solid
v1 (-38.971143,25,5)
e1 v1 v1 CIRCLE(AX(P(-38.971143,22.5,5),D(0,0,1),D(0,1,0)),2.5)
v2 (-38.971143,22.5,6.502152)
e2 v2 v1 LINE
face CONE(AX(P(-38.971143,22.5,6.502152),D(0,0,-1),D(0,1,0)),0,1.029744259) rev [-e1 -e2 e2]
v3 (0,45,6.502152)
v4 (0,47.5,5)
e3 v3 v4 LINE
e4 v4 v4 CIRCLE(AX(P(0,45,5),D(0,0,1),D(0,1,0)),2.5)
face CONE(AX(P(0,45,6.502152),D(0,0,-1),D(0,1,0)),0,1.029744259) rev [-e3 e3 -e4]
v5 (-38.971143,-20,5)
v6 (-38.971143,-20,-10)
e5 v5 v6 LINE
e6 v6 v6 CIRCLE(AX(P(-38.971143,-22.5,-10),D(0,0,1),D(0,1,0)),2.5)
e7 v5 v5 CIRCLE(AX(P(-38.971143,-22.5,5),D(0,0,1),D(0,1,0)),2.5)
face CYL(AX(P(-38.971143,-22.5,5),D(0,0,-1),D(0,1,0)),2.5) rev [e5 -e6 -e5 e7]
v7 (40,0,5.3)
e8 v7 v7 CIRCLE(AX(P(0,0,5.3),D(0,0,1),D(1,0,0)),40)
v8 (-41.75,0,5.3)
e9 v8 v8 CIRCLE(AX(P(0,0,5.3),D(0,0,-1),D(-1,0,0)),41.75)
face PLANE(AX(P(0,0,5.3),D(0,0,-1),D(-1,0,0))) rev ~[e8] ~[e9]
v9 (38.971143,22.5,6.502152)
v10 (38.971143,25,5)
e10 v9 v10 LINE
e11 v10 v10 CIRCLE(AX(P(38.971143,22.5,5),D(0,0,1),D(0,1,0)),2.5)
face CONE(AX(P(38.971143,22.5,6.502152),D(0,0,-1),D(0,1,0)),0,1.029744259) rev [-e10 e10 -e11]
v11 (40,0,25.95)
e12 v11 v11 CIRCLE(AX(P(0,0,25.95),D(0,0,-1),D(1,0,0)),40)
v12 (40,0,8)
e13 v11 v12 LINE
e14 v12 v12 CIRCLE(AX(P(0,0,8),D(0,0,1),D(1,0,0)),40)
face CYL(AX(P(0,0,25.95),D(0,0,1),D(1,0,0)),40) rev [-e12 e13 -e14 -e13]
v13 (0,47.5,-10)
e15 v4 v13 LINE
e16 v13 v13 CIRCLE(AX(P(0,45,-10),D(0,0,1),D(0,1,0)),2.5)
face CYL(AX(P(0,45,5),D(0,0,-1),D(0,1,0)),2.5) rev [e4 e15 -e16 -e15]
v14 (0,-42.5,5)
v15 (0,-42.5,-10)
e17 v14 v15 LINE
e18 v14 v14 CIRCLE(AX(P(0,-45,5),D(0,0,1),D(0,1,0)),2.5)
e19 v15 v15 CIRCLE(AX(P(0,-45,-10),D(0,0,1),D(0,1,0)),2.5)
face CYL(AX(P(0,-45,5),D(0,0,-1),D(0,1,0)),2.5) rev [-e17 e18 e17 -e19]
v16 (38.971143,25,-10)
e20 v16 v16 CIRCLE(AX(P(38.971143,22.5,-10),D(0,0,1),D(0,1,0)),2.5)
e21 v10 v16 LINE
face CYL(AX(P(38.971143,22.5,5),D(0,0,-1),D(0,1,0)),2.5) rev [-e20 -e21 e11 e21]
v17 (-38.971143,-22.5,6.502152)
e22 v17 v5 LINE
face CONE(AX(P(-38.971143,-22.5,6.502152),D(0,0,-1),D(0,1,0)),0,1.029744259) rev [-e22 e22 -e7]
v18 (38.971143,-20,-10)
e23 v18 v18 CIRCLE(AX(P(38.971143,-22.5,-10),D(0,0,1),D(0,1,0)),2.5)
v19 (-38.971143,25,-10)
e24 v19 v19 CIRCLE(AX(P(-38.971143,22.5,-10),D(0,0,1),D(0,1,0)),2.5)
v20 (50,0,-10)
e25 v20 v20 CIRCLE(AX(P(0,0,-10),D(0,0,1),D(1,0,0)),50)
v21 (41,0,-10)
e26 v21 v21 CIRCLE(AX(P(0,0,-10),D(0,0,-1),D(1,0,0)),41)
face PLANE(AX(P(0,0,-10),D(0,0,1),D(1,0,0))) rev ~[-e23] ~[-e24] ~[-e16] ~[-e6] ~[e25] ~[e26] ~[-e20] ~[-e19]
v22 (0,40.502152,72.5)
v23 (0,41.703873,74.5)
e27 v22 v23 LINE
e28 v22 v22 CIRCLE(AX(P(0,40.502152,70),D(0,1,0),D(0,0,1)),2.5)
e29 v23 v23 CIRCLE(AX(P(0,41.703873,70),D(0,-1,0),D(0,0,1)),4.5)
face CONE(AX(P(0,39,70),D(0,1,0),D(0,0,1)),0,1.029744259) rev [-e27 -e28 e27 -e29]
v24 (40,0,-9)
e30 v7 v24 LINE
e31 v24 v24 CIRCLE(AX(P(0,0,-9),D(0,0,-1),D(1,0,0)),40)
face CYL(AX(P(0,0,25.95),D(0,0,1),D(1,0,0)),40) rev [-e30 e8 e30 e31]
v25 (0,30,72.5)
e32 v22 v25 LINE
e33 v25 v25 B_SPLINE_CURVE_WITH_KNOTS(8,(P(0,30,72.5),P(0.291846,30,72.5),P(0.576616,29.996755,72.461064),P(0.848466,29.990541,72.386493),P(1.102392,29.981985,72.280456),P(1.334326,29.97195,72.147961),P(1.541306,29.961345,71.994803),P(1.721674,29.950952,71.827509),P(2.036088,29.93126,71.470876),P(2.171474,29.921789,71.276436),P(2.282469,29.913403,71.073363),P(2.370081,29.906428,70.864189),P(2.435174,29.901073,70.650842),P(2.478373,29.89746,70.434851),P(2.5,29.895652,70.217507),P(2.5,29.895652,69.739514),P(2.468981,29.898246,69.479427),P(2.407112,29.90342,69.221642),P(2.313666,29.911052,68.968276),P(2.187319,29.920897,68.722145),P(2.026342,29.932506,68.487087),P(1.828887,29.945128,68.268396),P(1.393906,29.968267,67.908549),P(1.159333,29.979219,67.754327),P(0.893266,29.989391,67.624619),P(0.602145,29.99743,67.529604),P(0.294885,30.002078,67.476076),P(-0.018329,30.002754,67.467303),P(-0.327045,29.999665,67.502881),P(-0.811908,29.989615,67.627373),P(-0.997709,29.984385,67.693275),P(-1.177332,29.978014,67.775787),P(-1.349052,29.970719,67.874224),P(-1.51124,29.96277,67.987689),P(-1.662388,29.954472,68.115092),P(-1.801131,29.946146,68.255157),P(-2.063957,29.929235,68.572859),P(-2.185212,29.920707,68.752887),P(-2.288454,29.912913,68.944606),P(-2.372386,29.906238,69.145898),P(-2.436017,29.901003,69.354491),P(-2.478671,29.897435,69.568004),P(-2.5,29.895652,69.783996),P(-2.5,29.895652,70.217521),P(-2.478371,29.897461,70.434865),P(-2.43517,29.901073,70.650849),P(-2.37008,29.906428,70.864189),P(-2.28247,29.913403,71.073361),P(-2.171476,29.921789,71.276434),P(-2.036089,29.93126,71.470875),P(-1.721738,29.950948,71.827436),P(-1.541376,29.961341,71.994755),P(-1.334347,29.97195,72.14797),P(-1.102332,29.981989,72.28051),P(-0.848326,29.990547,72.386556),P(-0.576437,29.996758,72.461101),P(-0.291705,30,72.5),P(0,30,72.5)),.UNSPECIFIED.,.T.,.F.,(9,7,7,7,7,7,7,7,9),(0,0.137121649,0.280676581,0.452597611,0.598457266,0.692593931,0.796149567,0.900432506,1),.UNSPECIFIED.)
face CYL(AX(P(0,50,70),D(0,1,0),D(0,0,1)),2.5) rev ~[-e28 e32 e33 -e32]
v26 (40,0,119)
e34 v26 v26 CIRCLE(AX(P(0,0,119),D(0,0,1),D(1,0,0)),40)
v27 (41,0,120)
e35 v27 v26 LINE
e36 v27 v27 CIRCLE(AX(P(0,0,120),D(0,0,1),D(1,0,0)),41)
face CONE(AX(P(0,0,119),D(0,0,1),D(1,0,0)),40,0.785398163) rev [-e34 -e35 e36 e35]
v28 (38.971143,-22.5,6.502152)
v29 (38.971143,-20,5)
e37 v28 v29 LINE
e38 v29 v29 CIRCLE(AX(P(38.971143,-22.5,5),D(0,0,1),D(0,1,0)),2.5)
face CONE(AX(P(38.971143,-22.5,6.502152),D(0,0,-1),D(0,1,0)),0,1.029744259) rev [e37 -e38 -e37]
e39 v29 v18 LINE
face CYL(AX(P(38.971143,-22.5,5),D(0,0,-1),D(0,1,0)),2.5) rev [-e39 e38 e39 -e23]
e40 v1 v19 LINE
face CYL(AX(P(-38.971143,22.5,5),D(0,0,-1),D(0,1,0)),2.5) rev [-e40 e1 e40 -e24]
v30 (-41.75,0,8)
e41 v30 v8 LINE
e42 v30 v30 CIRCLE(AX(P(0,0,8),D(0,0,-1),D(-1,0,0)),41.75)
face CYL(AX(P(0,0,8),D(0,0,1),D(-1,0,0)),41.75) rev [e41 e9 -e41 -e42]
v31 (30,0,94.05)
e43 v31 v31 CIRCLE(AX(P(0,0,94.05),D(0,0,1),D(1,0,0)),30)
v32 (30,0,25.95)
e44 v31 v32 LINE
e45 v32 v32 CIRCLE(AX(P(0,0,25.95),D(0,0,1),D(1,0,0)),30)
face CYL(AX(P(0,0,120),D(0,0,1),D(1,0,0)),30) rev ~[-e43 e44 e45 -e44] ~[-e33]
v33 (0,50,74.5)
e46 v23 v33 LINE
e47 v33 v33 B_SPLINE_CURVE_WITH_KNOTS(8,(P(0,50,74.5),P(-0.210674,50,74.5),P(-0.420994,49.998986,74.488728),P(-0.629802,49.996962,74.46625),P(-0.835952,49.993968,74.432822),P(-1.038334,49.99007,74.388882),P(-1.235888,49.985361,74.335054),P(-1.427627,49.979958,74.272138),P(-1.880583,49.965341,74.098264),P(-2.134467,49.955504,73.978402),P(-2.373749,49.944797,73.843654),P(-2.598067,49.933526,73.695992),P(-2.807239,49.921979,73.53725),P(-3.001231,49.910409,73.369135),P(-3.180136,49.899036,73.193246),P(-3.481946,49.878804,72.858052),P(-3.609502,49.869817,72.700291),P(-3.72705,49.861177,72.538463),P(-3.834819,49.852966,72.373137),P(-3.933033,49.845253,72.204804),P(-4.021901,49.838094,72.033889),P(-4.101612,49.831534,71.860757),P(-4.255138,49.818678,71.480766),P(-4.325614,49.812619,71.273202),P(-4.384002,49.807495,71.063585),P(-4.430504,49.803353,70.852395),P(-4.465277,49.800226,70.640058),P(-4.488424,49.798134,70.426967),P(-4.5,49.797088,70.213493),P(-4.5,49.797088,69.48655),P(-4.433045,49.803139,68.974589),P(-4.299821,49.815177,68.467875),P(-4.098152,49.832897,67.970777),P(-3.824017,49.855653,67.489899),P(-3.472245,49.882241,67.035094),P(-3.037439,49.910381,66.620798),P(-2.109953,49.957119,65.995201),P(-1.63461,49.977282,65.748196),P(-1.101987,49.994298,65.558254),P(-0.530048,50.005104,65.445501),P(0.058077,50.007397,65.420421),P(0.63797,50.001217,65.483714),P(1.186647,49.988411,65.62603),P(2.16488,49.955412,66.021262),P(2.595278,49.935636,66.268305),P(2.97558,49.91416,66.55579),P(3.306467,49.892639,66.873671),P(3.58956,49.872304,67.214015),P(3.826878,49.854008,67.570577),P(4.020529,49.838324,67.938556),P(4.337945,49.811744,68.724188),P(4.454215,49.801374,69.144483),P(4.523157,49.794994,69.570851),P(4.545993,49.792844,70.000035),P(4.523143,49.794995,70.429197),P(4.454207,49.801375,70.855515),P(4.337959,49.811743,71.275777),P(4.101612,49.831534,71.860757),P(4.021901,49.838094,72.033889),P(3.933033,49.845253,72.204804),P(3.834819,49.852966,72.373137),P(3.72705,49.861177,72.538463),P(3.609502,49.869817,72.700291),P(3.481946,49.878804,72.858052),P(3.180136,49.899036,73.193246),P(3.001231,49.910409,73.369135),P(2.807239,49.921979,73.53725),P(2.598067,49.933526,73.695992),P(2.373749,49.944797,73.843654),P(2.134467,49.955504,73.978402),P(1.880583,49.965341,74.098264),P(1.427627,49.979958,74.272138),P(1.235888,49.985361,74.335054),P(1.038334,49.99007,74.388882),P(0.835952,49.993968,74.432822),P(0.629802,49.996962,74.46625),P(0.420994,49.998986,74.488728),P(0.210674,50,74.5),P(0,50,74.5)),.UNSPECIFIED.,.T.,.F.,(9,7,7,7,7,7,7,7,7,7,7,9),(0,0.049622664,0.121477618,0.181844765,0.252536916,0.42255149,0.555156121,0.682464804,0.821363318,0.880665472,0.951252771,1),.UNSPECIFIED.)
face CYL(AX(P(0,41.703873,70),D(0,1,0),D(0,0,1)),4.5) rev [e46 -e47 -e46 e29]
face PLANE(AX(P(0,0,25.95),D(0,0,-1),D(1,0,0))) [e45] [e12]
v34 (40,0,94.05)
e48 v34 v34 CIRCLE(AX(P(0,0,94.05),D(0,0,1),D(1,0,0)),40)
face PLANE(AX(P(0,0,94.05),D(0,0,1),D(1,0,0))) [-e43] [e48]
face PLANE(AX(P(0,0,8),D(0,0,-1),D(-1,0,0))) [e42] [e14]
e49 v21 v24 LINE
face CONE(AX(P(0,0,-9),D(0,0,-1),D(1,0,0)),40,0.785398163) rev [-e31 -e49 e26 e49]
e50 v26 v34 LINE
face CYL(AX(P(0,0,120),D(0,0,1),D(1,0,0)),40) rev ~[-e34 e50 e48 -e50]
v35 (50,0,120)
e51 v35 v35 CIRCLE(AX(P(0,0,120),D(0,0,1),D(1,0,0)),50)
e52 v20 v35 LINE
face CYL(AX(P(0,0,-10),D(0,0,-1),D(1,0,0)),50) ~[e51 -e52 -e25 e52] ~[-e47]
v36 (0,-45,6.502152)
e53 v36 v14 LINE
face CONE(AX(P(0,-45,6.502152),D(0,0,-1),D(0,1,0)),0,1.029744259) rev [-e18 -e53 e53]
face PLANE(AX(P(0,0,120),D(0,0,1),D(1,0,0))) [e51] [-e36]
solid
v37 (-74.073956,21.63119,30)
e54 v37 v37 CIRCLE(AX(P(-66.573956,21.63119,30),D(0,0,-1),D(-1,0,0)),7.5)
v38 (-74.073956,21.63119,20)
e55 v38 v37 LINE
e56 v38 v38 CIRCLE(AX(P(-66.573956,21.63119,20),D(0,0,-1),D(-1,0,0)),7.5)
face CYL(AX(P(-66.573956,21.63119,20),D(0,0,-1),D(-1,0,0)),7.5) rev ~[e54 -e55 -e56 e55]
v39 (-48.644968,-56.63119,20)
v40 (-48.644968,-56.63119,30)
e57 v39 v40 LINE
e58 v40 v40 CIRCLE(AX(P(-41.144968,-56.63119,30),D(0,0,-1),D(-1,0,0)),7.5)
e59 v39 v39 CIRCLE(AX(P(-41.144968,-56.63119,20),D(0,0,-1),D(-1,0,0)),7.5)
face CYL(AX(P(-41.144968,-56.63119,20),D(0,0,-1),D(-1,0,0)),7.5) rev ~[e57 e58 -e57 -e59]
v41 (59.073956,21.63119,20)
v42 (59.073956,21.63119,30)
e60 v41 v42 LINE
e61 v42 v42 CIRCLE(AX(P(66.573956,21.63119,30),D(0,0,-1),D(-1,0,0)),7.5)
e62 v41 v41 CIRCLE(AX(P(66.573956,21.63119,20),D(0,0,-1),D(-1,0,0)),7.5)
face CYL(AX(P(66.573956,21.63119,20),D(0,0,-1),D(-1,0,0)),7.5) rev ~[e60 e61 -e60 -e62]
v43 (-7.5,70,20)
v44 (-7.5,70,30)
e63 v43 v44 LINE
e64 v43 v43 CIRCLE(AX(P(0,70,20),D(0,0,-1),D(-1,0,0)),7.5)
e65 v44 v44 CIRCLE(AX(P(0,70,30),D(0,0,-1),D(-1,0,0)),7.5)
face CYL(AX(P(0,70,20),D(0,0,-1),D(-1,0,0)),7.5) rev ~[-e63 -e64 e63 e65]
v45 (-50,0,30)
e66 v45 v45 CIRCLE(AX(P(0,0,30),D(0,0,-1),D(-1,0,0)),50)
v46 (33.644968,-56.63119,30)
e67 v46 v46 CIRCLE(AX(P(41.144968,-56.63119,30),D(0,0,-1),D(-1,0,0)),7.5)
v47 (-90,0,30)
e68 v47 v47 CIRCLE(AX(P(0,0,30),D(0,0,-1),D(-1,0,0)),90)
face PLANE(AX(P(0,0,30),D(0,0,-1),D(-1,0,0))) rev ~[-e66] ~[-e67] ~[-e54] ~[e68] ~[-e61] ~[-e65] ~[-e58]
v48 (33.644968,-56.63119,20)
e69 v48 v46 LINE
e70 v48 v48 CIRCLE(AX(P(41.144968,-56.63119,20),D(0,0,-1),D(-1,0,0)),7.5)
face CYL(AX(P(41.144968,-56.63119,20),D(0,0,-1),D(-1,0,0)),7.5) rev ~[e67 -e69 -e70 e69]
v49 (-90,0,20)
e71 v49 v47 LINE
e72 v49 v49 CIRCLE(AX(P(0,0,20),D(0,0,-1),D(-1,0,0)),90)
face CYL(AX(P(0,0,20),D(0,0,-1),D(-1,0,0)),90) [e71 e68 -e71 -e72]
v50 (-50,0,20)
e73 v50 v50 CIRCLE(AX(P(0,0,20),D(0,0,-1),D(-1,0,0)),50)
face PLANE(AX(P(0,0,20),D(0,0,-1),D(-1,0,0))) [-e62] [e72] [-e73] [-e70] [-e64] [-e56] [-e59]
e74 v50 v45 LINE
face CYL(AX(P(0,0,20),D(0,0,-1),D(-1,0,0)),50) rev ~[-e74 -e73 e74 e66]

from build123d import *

# Parameters (mm, degrees)
EXTRUDE_1_DEPTH             = 120
EXTRUDE_1_DEPTH_BACK        = 10
SKETCH_1_R                  = 50
SKETCH_2_R                  = 30
CUT_EXTRUDE_1_DEPTH         = 120
SKETCH_3_R                  = 40
CUT_EXTRUDE_2_DEPTH         = 25.95
CUT_EXTRUDE_START           = -35.95
SKETCH_4_R                  = 40
CUT_EXTRUDE_3_DEPTH         = 35.95
SKETCH_6_R                  = 90
SKETCH_6_R_2                = 50
EXTRUDE_2_DEPTH             = 10
SKETCH_7_R                  = 2.5
CUT_EXTRUDE_5_DEPTH         = 30
SKETCH_11_R                 = 7.5
CUT_EXTRUDE_6_DEPTH         = 10
CUT_EXTRUDE_START_2         = -2.7
SKETCH_12_R                 = 41.75
SKETCH_12_R_2               = 40
CUT_EXTRUDE_7_DEPTH         = 2.7
HOLE_WIZARD_M6_1_AT_2_COUNT = 2
HOLE_WIZARD_M6_1_AT_2_PITCH = 45
HOLE_WIZARD_M6_1_AT_3_COUNT = 2
HOLE_WIZARD_M6_1_AT_3_PITCH = 77.942286341
HOLE_WIZARD_M6_1_AT_4_COUNT = 2
HOLE_WIZARD_M6_1_AT_4_PITCH = 90
HOLE_WIZARD_M6_1_AT_5_COUNT = 2
HOLE_WIZARD_M6_1_AT_5_PITCH = 77.942286341
HOLE_WIZARD_M6_1_AT_6_COUNT = 2
HOLE_WIZARD_M6_1_AT_6_PITCH = 45
CHAMFER_1_SIZE              = 1


with BuildPart() as part:
    # 草图1 → 凸台-拉伸1 (new, two sides: drawn at the far end of the back side and taken through both)
    with BuildSketch(Plane.XY.offset(-EXTRUDE_1_DEPTH_BACK)):
        Circle(SKETCH_1_R)
    extrude(amount=EXTRUDE_1_DEPTH + EXTRUDE_1_DEPTH_BACK)

    # 草图2 → 切除-拉伸1 (cut)
    with BuildSketch(Plane.XY.offset(120)):
        Circle(SKETCH_2_R)
    extrude(amount=-CUT_EXTRUDE_1_DEPTH, mode=Mode.SUBTRACT)

    # 草图3 → 切除-拉伸2 (cut)
    with BuildSketch(Plane.XY.offset(120)):
        Circle(SKETCH_3_R)
    extrude(amount=-CUT_EXTRUDE_2_DEPTH, mode=Mode.SUBTRACT)

    # 草图4 → 切除-拉伸3 (cut)
    with BuildSketch(Plane(origin=(0, 0, -10), x_dir=(-1, 0, 0), z_dir=(0, 0, -1)).offset(CUT_EXTRUDE_START)):
        with Locations(Location((0, 0, 0), (0, 0, 180))):
            Circle(SKETCH_4_R)
    extrude(amount=CUT_EXTRUDE_3_DEPTH, mode=Mode.SUBTRACT)

    # 草图7 → 切除-拉伸5 (cut)
    with BuildSketch(Plane(origin=(0, 50, 0), x_dir=(1, 0, 0), z_dir=(0, 1, 0))):
        with Locations(Location((0, -70, 0), (0, 0, 270))):
            Circle(SKETCH_7_R)
    extrude(amount=-CUT_EXTRUDE_5_DEPTH, mode=Mode.SUBTRACT)

    # 草图8 → M10x1.0 螺纹孔1 (revolve, cut)
    with BuildSketch(Plane(origin=(0, 50, 70), x_dir=(0, 0, 1), z_dir=(1, 0, 0))):
        Polygon((0, 0), (0, 11), (4.5, 8.296127214), (4.5, 0), align=None)
    revolve(axis=Axis((0, 56.35, 70), (0, -1, 0)), mode=Mode.SUBTRACT)

    # 草图12 → 切除-拉伸7 (cut)
    with BuildSketch(Plane(origin=(0, 0, 5.3), x_dir=(-1, 0, 0), z_dir=(0, 0, -1)).offset(CUT_EXTRUDE_START_2)):
        Circle(SKETCH_12_R)
        Circle(SKETCH_12_R_2, mode=Mode.SUBTRACT)
    extrude(amount=CUT_EXTRUDE_7_DEPTH, mode=Mode.SUBTRACT)

    # 草图17 → M6 螺纹孔1 (revolve, cut)
    with BuildSketch(Plane(origin=(0, 45, -10), x_dir=(0, 1, 0), z_dir=(1, 0, 0))):
        Polygon((0, 0), (0, 16.502151548), (2.5, 15), (2.5, 0), align=None)
    hole_wizard_m6_1 = revolve(axis=Axis((0, 45, -16.35), (0, 0, 1)), mode=Mode.SUBTRACT)

    # M6 螺纹孔1 at 2: M6 螺纹孔1 ×2
    with Locations(*[Vector(-0.8660254037844528, -0.4999999999999755, 0) * (i * HOLE_WIZARD_M6_1_AT_2_PITCH) for i in range(1, HOLE_WIZARD_M6_1_AT_2_COUNT)]):
        add(hole_wizard_m6_1, mode=Mode.SUBTRACT)

    # M6 螺纹孔1 at 3: M6 螺纹孔1 ×2
    with Locations(*[Vector(-0.5000000000000245, -0.8660254037844246, 0) * (i * HOLE_WIZARD_M6_1_AT_3_PITCH) for i in range(1, HOLE_WIZARD_M6_1_AT_3_COUNT)]):
        add(hole_wizard_m6_1, mode=Mode.SUBTRACT)

    # M6 螺纹孔1 at 4: M6 螺纹孔1 ×2
    with Locations(*[(0, -i * HOLE_WIZARD_M6_1_AT_4_PITCH, 0) for i in range(1, HOLE_WIZARD_M6_1_AT_4_COUNT)]):
        add(hole_wizard_m6_1, mode=Mode.SUBTRACT)

    # M6 螺纹孔1 at 5: M6 螺纹孔1 ×2
    with Locations(*[Vector(0.4999999999999754, -0.8660254037844529, 0) * (i * HOLE_WIZARD_M6_1_AT_5_PITCH) for i in range(1, HOLE_WIZARD_M6_1_AT_5_COUNT)]):
        add(hole_wizard_m6_1, mode=Mode.SUBTRACT)

    # M6 螺纹孔1 at 6: M6 螺纹孔1 ×2
    with Locations(*[Vector(0.8660254037844243, -0.500000000000025, 0) * (i * HOLE_WIZARD_M6_1_AT_6_PITCH) for i in range(1, HOLE_WIZARD_M6_1_AT_6_COUNT)]):
        add(hole_wizard_m6_1, mode=Mode.SUBTRACT)

    # 倒角1
    chamfer_1_edges = [part.edges().sort_by_distance(p)[0] for p in [
        (-40, 0, 120),
        (-40, 0, -10),
    ]]
    chamfer(chamfer_1_edges, length=CHAMFER_1_SIZE)


with BuildPart() as body_2:
    # 草图6 → 凸台-拉伸2 (new body)
    with BuildSketch(Plane(origin=(0, 0, 20), x_dir=(-1, 0, 0), z_dir=(0, 0, -1))):
        Circle(SKETCH_6_R)
        Circle(SKETCH_6_R_2, mode=Mode.SUBTRACT)
    extrude(amount=-EXTRUDE_2_DEPTH)

    # 草图11 → 切除-拉伸6 (cut)
    with BuildSketch(Plane(origin=(0, 0, 20), x_dir=(-1, 0, 0), z_dir=(0, 0, -1))):
        with Locations((0, 70)):
            Circle(SKETCH_11_R)
        with Locations((66.573956141, 21.631189606)):
            Circle(SKETCH_11_R)
        with Locations((41.14496766, -56.631189606)):
            Circle(SKETCH_11_R)
        with Locations((-41.14496766, -56.631189606)):
            Circle(SKETCH_11_R)
        with Locations((-66.573956141, 21.631189606)):
            Circle(SKETCH_11_R)
    extrude(amount=-CUT_EXTRUDE_6_DEPTH, mode=Mode.SUBTRACT)


solid = Compound([part.part, body_2.part])
